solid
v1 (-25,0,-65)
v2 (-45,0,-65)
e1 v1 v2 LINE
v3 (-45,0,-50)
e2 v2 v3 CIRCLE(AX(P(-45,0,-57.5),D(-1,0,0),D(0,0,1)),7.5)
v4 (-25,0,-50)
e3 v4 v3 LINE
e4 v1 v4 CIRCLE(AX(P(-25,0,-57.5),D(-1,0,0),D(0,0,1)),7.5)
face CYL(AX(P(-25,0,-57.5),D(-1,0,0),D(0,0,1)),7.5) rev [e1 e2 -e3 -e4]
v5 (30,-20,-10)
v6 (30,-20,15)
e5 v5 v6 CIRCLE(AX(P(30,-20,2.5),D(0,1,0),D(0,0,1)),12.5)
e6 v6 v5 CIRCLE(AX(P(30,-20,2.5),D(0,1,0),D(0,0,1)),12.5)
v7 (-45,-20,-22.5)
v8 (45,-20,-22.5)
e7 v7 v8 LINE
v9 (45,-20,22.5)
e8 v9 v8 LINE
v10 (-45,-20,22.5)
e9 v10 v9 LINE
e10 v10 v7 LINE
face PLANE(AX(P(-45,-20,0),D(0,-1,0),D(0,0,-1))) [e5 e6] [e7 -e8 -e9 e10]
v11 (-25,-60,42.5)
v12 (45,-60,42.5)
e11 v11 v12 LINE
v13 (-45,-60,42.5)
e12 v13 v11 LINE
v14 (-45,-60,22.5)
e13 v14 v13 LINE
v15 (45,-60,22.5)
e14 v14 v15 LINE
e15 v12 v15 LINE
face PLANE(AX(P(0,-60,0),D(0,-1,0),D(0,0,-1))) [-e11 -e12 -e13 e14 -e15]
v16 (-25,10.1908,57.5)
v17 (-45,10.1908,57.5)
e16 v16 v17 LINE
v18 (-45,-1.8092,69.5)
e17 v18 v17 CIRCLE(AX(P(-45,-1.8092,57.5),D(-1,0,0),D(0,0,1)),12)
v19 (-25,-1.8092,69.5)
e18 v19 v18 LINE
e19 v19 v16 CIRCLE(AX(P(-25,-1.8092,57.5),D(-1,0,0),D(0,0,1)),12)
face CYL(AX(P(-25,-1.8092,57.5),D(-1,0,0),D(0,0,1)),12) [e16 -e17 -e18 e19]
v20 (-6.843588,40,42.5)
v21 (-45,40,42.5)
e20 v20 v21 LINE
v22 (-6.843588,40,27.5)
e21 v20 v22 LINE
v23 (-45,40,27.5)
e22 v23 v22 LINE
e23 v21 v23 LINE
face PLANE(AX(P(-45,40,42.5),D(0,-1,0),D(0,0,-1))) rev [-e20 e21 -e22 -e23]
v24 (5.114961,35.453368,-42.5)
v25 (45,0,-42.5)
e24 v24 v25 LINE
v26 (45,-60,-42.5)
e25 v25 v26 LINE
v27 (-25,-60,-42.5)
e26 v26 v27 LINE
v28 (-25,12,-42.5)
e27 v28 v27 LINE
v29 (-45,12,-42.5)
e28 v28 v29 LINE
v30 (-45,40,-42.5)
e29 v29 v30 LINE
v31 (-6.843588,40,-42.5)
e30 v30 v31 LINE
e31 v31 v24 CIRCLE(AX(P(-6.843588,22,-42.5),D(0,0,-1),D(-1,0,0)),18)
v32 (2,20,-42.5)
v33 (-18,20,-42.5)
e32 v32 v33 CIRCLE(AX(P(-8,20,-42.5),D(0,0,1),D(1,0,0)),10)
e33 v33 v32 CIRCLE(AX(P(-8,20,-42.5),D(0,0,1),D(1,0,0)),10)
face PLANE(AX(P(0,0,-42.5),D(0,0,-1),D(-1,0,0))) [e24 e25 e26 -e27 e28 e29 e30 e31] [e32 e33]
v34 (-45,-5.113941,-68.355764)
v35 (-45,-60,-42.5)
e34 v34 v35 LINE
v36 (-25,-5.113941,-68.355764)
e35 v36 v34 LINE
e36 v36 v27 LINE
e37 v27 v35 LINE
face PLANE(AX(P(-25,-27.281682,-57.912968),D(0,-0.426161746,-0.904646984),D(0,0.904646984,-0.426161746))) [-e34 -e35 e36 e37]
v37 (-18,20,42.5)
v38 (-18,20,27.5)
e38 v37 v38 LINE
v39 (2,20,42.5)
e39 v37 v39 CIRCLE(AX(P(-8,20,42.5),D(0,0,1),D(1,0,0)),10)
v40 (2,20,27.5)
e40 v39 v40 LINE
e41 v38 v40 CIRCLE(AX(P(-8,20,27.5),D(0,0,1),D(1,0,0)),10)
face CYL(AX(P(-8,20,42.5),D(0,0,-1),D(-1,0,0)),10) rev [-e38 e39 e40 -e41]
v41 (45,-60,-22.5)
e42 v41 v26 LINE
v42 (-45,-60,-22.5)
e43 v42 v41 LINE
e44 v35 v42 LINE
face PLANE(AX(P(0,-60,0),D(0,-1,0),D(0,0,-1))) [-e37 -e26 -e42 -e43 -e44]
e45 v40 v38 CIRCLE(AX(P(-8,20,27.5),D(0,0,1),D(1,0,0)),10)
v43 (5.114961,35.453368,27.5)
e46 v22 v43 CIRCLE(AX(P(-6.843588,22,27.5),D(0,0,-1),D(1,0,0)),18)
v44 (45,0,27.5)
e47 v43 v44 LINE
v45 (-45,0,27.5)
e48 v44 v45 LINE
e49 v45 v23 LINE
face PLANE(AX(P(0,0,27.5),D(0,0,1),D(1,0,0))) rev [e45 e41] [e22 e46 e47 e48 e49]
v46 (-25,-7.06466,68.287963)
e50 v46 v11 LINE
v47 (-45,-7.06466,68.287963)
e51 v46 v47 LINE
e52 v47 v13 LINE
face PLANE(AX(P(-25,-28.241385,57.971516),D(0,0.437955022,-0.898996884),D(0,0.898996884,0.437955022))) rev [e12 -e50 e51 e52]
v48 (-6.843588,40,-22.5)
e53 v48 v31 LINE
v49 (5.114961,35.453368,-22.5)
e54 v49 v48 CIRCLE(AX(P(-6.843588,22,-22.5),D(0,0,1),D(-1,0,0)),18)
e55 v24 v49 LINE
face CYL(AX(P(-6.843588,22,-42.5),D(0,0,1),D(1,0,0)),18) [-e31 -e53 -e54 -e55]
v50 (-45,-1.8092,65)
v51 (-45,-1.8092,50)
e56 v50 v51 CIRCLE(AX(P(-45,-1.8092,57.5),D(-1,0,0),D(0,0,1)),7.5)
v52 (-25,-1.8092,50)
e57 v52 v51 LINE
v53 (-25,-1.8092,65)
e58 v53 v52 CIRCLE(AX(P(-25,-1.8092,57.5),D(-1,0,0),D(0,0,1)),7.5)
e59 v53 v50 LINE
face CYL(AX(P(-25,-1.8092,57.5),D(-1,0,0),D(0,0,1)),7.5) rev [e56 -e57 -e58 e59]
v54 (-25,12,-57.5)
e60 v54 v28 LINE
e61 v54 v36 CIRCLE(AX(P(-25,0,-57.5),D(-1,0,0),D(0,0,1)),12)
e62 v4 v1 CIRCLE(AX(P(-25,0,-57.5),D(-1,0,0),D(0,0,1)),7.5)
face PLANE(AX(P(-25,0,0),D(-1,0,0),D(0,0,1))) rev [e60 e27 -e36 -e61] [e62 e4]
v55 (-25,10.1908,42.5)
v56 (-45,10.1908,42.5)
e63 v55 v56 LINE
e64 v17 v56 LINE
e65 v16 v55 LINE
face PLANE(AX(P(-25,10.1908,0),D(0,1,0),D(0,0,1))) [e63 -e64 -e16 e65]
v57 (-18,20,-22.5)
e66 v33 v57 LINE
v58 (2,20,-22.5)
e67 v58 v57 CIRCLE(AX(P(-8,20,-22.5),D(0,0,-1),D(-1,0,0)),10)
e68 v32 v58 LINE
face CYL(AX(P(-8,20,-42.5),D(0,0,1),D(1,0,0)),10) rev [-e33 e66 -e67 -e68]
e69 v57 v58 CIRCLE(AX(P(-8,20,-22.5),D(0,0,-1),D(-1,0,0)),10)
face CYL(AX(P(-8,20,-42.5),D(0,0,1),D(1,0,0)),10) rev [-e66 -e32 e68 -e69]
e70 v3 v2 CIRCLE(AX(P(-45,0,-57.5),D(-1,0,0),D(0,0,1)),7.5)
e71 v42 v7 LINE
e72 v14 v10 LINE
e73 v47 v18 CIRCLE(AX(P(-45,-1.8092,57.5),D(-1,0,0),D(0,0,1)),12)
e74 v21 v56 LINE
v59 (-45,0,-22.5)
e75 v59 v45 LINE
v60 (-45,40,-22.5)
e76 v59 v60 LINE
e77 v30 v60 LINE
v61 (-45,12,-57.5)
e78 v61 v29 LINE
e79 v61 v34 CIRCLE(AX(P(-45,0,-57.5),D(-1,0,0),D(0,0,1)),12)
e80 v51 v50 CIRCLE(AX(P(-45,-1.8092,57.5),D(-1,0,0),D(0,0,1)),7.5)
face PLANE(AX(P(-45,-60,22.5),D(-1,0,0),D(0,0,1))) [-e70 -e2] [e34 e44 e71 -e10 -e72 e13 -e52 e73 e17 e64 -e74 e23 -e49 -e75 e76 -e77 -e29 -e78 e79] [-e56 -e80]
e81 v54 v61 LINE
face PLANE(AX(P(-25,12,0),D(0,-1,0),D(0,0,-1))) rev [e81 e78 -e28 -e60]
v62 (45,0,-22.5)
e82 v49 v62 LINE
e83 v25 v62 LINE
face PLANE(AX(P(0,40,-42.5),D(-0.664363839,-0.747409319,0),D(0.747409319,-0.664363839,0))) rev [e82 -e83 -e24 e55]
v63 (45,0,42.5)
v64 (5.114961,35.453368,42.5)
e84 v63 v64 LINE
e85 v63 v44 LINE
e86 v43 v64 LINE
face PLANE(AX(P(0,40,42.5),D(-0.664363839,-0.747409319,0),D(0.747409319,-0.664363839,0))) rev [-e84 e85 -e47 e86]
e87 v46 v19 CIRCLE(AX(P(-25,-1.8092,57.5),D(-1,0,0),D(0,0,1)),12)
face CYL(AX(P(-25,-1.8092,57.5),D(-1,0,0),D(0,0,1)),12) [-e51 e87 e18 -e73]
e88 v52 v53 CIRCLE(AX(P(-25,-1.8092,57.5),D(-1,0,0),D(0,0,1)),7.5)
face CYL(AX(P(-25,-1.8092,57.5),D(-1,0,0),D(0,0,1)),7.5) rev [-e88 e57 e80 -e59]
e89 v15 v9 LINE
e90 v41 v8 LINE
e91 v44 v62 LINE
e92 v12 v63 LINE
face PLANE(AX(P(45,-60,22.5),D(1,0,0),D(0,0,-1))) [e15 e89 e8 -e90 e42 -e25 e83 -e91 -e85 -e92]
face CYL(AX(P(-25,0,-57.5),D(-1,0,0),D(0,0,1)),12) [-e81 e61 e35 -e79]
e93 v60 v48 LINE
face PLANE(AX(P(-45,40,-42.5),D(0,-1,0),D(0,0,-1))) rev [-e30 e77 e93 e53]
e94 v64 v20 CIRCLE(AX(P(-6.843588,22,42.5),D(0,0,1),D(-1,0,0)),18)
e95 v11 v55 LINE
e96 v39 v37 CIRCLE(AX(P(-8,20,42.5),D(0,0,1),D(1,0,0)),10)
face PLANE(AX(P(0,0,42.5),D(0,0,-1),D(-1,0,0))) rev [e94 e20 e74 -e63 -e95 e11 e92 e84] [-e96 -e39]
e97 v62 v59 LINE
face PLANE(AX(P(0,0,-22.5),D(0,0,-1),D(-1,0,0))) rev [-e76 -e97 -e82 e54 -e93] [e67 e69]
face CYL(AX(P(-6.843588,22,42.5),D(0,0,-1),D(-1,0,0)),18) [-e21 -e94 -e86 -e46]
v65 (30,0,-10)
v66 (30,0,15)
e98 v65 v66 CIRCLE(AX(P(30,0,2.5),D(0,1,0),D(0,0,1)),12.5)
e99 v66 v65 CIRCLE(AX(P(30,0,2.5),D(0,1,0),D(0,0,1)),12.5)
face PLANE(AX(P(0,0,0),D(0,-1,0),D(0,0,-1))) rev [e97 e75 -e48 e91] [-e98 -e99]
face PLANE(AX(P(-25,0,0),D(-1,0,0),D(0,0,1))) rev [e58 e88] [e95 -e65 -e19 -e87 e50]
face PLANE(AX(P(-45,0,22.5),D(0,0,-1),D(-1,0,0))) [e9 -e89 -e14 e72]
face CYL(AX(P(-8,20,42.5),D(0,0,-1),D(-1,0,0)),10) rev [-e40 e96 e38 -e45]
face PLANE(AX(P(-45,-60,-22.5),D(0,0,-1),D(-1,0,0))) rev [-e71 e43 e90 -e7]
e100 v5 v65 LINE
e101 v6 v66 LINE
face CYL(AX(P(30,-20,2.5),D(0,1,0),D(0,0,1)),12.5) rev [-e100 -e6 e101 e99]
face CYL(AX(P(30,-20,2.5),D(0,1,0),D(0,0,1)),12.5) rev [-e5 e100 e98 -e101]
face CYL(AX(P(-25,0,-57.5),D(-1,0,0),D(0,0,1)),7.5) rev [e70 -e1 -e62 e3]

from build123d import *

# Parameters (mm, degrees)
BASE_BLOCK_SKETCH_W       = 90
BASE_BLOCK_SKETCH_H       = 45
BASE_BLOCK_90X45X60_DEPTH = 60
LUG_A_SKETCH_R            = 10
LUG_A_DEPTH               = 20
LUG_RECESS_CUT_DEPTH      = 5
LUG_B_DEPTH               = 20
LUG_HOLE_SKETCH_R         = 10
LUG_HOLES_DEPTH           = 114.357840488
ANGLED_SIDE_CUT_SKETCH_W  = 35
ANGLED_SIDE_CUT_SKETCH_H  = 40
ANGLED_SIDE_CUT_DEPTH     = 117.216392992
SIDE_BOSS_A_SKETCH_R      = 7.5
SIDE_BOSS_A_DEPTH         = 20
SIDE_BOSS_B_SKETCH_R      = 7.5
SIDE_BOSS_B_DEPTH         = 20
TOP_HOLE_SKETCH_R         = 12.5
TOP_HOLE_DEPTH            = 20
LUG_TOP_FILLET_R18_R      = 18
BOTTOM_SLOT_SKETCH_W      = 10
BOTTOM_SLOT_SKETCH_H      = 40
BOTTOM_SLOT_DEPTH         = 129.570019834


with BuildPart() as part:
    # Base Block Sketch → Base Block 90x45x60 (new body)
    with BuildSketch(Plane(origin=(0, 0, 0), x_dir=(1, 0, 0), z_dir=(0, 1, 0))):
        Rectangle(BASE_BLOCK_SKETCH_W, BASE_BLOCK_SKETCH_H)
    extrude(amount=-BASE_BLOCK_90X45X60_DEPTH)

    # Lug A Sketch → Lug A (add)
    with BuildSketch(Plane.XY.offset(22.5)):
        Polygon((-45, 0), (-45, -60), (45, -60), (45, 0), (0, 40), (-45, 40), align=None)
        with Locations((-8, 20)):
            Circle(LUG_A_SKETCH_R, mode=Mode.SUBTRACT)
    extrude(amount=LUG_A_DEPTH)

    # Lug Recess Sketch → Lug Recess Cut (cut)
    with BuildSketch(Plane(origin=(0, 0, 22.5), x_dir=(-1, 0, 0), z_dir=(0, 0, -1))):
        Polygon((-45, 0), (45, 0), (45, 40), (0, 40), align=None)
    extrude(amount=-LUG_RECESS_CUT_DEPTH, mode=Mode.SUBTRACT)

    # Lug B Sketch → Lug B (add)
    with BuildSketch(Plane(origin=(0, 0, -22.5), x_dir=(-1, 0, 0), z_dir=(0, 0, -1))):
        Polygon((-45, 0), (-45, -60), (45, -60), (45, 0), (45, 40), (0, 40), align=None)
    extrude(amount=LUG_B_DEPTH)

    # Lug Hole Sketch → Lug Holes (cut, through all)
    with BuildSketch(Plane.XY.offset(42.5)):
        with Locations((-8, 20)):
            Circle(LUG_HOLE_SKETCH_R)
    extrude(amount=-LUG_HOLES_DEPTH, mode=Mode.SUBTRACT)

    # Angled Side Cut Sketch → Angled Side Cut (cut, through all)
    with BuildSketch(Plane(origin=(45, 0, 0), x_dir=(0, 0, -1), z_dir=(1, 0, 0))):
        with Locations((-5, -40)):
            Rectangle(ANGLED_SIDE_CUT_SKETCH_W, ANGLED_SIDE_CUT_SKETCH_H)
    extrude(amount=-ANGLED_SIDE_CUT_DEPTH, mode=Mode.SUBTRACT)

    # Side Boss A Sketch → Side Boss A (add)
    with BuildSketch(Plane.ZY.offset(45)):
        with BuildLine():
            ThreePointArc((68.287962614, -7.064659931), (67.675104993, 4.552186853), (57.5, 10.190800338))
            Line((57.5, 10.190800338), (42.5, 10.190800338))
            Line((42.5, 10.190800338), (42.5, -60))
            Line((42.5, -60), (68.287962614, -7.064659931))
        make_face()
        with Locations((57.5, -1.809199662)):
            Circle(SIDE_BOSS_A_SKETCH_R, mode=Mode.SUBTRACT)
    extrude(amount=-SIDE_BOSS_A_DEPTH)

    # Side Boss B Sketch → Side Boss B (add)
    with BuildSketch(Plane.ZY.offset(45)):
        with BuildLine():
            Line((-42.5, 12), (-57.5, 12))
            ThreePointArc((-57.5, 12), (-67.633293922, 6.427779888), (-68.355763811, -5.113940953))
            Line((-68.355763811, -5.113940953), (-42.5, -60))
            Line((-42.5, -60), (-42.5, 12))
        make_face()
        with Locations((-57.5, 0)):
            Circle(SIDE_BOSS_B_SKETCH_R, mode=Mode.SUBTRACT)
    extrude(amount=-SIDE_BOSS_B_DEPTH)

    # Top Hole Sketch → Top Hole (cut)
    with BuildSketch(Plane(origin=(0, 0, 0), x_dir=(1, 0, 0), z_dir=(0, 1, 0))):
        with Locations(Location((30, -2.5, 0), (0, 0, 270))):
            Circle(TOP_HOLE_SKETCH_R)
    extrude(amount=-TOP_HOLE_DEPTH, mode=Mode.SUBTRACT)

    # Lug Top Fillet R18
    lug_top_fillet_r18_edges = [part.edges().sort_by_distance(p)[0] for p in [
        (0, 40, 35),
        (0, 40, -32.5),
    ]]
    fillet(lug_top_fillet_r18_edges, radius=LUG_TOP_FILLET_R18_R)

    # Bottom Slot Sketch → Bottom Slot (cut, through all)
    with BuildSketch(Plane(origin=(45, 0, 0), x_dir=(0, 0, -1), z_dir=(1, 0, 0))):
        with Locations((17.5, -40)):
            Rectangle(BOTTOM_SLOT_SKETCH_W, BOTTOM_SLOT_SKETCH_H)
    extrude(amount=-BOTTOM_SLOT_DEPTH, mode=Mode.SUBTRACT)


solid = part.part
